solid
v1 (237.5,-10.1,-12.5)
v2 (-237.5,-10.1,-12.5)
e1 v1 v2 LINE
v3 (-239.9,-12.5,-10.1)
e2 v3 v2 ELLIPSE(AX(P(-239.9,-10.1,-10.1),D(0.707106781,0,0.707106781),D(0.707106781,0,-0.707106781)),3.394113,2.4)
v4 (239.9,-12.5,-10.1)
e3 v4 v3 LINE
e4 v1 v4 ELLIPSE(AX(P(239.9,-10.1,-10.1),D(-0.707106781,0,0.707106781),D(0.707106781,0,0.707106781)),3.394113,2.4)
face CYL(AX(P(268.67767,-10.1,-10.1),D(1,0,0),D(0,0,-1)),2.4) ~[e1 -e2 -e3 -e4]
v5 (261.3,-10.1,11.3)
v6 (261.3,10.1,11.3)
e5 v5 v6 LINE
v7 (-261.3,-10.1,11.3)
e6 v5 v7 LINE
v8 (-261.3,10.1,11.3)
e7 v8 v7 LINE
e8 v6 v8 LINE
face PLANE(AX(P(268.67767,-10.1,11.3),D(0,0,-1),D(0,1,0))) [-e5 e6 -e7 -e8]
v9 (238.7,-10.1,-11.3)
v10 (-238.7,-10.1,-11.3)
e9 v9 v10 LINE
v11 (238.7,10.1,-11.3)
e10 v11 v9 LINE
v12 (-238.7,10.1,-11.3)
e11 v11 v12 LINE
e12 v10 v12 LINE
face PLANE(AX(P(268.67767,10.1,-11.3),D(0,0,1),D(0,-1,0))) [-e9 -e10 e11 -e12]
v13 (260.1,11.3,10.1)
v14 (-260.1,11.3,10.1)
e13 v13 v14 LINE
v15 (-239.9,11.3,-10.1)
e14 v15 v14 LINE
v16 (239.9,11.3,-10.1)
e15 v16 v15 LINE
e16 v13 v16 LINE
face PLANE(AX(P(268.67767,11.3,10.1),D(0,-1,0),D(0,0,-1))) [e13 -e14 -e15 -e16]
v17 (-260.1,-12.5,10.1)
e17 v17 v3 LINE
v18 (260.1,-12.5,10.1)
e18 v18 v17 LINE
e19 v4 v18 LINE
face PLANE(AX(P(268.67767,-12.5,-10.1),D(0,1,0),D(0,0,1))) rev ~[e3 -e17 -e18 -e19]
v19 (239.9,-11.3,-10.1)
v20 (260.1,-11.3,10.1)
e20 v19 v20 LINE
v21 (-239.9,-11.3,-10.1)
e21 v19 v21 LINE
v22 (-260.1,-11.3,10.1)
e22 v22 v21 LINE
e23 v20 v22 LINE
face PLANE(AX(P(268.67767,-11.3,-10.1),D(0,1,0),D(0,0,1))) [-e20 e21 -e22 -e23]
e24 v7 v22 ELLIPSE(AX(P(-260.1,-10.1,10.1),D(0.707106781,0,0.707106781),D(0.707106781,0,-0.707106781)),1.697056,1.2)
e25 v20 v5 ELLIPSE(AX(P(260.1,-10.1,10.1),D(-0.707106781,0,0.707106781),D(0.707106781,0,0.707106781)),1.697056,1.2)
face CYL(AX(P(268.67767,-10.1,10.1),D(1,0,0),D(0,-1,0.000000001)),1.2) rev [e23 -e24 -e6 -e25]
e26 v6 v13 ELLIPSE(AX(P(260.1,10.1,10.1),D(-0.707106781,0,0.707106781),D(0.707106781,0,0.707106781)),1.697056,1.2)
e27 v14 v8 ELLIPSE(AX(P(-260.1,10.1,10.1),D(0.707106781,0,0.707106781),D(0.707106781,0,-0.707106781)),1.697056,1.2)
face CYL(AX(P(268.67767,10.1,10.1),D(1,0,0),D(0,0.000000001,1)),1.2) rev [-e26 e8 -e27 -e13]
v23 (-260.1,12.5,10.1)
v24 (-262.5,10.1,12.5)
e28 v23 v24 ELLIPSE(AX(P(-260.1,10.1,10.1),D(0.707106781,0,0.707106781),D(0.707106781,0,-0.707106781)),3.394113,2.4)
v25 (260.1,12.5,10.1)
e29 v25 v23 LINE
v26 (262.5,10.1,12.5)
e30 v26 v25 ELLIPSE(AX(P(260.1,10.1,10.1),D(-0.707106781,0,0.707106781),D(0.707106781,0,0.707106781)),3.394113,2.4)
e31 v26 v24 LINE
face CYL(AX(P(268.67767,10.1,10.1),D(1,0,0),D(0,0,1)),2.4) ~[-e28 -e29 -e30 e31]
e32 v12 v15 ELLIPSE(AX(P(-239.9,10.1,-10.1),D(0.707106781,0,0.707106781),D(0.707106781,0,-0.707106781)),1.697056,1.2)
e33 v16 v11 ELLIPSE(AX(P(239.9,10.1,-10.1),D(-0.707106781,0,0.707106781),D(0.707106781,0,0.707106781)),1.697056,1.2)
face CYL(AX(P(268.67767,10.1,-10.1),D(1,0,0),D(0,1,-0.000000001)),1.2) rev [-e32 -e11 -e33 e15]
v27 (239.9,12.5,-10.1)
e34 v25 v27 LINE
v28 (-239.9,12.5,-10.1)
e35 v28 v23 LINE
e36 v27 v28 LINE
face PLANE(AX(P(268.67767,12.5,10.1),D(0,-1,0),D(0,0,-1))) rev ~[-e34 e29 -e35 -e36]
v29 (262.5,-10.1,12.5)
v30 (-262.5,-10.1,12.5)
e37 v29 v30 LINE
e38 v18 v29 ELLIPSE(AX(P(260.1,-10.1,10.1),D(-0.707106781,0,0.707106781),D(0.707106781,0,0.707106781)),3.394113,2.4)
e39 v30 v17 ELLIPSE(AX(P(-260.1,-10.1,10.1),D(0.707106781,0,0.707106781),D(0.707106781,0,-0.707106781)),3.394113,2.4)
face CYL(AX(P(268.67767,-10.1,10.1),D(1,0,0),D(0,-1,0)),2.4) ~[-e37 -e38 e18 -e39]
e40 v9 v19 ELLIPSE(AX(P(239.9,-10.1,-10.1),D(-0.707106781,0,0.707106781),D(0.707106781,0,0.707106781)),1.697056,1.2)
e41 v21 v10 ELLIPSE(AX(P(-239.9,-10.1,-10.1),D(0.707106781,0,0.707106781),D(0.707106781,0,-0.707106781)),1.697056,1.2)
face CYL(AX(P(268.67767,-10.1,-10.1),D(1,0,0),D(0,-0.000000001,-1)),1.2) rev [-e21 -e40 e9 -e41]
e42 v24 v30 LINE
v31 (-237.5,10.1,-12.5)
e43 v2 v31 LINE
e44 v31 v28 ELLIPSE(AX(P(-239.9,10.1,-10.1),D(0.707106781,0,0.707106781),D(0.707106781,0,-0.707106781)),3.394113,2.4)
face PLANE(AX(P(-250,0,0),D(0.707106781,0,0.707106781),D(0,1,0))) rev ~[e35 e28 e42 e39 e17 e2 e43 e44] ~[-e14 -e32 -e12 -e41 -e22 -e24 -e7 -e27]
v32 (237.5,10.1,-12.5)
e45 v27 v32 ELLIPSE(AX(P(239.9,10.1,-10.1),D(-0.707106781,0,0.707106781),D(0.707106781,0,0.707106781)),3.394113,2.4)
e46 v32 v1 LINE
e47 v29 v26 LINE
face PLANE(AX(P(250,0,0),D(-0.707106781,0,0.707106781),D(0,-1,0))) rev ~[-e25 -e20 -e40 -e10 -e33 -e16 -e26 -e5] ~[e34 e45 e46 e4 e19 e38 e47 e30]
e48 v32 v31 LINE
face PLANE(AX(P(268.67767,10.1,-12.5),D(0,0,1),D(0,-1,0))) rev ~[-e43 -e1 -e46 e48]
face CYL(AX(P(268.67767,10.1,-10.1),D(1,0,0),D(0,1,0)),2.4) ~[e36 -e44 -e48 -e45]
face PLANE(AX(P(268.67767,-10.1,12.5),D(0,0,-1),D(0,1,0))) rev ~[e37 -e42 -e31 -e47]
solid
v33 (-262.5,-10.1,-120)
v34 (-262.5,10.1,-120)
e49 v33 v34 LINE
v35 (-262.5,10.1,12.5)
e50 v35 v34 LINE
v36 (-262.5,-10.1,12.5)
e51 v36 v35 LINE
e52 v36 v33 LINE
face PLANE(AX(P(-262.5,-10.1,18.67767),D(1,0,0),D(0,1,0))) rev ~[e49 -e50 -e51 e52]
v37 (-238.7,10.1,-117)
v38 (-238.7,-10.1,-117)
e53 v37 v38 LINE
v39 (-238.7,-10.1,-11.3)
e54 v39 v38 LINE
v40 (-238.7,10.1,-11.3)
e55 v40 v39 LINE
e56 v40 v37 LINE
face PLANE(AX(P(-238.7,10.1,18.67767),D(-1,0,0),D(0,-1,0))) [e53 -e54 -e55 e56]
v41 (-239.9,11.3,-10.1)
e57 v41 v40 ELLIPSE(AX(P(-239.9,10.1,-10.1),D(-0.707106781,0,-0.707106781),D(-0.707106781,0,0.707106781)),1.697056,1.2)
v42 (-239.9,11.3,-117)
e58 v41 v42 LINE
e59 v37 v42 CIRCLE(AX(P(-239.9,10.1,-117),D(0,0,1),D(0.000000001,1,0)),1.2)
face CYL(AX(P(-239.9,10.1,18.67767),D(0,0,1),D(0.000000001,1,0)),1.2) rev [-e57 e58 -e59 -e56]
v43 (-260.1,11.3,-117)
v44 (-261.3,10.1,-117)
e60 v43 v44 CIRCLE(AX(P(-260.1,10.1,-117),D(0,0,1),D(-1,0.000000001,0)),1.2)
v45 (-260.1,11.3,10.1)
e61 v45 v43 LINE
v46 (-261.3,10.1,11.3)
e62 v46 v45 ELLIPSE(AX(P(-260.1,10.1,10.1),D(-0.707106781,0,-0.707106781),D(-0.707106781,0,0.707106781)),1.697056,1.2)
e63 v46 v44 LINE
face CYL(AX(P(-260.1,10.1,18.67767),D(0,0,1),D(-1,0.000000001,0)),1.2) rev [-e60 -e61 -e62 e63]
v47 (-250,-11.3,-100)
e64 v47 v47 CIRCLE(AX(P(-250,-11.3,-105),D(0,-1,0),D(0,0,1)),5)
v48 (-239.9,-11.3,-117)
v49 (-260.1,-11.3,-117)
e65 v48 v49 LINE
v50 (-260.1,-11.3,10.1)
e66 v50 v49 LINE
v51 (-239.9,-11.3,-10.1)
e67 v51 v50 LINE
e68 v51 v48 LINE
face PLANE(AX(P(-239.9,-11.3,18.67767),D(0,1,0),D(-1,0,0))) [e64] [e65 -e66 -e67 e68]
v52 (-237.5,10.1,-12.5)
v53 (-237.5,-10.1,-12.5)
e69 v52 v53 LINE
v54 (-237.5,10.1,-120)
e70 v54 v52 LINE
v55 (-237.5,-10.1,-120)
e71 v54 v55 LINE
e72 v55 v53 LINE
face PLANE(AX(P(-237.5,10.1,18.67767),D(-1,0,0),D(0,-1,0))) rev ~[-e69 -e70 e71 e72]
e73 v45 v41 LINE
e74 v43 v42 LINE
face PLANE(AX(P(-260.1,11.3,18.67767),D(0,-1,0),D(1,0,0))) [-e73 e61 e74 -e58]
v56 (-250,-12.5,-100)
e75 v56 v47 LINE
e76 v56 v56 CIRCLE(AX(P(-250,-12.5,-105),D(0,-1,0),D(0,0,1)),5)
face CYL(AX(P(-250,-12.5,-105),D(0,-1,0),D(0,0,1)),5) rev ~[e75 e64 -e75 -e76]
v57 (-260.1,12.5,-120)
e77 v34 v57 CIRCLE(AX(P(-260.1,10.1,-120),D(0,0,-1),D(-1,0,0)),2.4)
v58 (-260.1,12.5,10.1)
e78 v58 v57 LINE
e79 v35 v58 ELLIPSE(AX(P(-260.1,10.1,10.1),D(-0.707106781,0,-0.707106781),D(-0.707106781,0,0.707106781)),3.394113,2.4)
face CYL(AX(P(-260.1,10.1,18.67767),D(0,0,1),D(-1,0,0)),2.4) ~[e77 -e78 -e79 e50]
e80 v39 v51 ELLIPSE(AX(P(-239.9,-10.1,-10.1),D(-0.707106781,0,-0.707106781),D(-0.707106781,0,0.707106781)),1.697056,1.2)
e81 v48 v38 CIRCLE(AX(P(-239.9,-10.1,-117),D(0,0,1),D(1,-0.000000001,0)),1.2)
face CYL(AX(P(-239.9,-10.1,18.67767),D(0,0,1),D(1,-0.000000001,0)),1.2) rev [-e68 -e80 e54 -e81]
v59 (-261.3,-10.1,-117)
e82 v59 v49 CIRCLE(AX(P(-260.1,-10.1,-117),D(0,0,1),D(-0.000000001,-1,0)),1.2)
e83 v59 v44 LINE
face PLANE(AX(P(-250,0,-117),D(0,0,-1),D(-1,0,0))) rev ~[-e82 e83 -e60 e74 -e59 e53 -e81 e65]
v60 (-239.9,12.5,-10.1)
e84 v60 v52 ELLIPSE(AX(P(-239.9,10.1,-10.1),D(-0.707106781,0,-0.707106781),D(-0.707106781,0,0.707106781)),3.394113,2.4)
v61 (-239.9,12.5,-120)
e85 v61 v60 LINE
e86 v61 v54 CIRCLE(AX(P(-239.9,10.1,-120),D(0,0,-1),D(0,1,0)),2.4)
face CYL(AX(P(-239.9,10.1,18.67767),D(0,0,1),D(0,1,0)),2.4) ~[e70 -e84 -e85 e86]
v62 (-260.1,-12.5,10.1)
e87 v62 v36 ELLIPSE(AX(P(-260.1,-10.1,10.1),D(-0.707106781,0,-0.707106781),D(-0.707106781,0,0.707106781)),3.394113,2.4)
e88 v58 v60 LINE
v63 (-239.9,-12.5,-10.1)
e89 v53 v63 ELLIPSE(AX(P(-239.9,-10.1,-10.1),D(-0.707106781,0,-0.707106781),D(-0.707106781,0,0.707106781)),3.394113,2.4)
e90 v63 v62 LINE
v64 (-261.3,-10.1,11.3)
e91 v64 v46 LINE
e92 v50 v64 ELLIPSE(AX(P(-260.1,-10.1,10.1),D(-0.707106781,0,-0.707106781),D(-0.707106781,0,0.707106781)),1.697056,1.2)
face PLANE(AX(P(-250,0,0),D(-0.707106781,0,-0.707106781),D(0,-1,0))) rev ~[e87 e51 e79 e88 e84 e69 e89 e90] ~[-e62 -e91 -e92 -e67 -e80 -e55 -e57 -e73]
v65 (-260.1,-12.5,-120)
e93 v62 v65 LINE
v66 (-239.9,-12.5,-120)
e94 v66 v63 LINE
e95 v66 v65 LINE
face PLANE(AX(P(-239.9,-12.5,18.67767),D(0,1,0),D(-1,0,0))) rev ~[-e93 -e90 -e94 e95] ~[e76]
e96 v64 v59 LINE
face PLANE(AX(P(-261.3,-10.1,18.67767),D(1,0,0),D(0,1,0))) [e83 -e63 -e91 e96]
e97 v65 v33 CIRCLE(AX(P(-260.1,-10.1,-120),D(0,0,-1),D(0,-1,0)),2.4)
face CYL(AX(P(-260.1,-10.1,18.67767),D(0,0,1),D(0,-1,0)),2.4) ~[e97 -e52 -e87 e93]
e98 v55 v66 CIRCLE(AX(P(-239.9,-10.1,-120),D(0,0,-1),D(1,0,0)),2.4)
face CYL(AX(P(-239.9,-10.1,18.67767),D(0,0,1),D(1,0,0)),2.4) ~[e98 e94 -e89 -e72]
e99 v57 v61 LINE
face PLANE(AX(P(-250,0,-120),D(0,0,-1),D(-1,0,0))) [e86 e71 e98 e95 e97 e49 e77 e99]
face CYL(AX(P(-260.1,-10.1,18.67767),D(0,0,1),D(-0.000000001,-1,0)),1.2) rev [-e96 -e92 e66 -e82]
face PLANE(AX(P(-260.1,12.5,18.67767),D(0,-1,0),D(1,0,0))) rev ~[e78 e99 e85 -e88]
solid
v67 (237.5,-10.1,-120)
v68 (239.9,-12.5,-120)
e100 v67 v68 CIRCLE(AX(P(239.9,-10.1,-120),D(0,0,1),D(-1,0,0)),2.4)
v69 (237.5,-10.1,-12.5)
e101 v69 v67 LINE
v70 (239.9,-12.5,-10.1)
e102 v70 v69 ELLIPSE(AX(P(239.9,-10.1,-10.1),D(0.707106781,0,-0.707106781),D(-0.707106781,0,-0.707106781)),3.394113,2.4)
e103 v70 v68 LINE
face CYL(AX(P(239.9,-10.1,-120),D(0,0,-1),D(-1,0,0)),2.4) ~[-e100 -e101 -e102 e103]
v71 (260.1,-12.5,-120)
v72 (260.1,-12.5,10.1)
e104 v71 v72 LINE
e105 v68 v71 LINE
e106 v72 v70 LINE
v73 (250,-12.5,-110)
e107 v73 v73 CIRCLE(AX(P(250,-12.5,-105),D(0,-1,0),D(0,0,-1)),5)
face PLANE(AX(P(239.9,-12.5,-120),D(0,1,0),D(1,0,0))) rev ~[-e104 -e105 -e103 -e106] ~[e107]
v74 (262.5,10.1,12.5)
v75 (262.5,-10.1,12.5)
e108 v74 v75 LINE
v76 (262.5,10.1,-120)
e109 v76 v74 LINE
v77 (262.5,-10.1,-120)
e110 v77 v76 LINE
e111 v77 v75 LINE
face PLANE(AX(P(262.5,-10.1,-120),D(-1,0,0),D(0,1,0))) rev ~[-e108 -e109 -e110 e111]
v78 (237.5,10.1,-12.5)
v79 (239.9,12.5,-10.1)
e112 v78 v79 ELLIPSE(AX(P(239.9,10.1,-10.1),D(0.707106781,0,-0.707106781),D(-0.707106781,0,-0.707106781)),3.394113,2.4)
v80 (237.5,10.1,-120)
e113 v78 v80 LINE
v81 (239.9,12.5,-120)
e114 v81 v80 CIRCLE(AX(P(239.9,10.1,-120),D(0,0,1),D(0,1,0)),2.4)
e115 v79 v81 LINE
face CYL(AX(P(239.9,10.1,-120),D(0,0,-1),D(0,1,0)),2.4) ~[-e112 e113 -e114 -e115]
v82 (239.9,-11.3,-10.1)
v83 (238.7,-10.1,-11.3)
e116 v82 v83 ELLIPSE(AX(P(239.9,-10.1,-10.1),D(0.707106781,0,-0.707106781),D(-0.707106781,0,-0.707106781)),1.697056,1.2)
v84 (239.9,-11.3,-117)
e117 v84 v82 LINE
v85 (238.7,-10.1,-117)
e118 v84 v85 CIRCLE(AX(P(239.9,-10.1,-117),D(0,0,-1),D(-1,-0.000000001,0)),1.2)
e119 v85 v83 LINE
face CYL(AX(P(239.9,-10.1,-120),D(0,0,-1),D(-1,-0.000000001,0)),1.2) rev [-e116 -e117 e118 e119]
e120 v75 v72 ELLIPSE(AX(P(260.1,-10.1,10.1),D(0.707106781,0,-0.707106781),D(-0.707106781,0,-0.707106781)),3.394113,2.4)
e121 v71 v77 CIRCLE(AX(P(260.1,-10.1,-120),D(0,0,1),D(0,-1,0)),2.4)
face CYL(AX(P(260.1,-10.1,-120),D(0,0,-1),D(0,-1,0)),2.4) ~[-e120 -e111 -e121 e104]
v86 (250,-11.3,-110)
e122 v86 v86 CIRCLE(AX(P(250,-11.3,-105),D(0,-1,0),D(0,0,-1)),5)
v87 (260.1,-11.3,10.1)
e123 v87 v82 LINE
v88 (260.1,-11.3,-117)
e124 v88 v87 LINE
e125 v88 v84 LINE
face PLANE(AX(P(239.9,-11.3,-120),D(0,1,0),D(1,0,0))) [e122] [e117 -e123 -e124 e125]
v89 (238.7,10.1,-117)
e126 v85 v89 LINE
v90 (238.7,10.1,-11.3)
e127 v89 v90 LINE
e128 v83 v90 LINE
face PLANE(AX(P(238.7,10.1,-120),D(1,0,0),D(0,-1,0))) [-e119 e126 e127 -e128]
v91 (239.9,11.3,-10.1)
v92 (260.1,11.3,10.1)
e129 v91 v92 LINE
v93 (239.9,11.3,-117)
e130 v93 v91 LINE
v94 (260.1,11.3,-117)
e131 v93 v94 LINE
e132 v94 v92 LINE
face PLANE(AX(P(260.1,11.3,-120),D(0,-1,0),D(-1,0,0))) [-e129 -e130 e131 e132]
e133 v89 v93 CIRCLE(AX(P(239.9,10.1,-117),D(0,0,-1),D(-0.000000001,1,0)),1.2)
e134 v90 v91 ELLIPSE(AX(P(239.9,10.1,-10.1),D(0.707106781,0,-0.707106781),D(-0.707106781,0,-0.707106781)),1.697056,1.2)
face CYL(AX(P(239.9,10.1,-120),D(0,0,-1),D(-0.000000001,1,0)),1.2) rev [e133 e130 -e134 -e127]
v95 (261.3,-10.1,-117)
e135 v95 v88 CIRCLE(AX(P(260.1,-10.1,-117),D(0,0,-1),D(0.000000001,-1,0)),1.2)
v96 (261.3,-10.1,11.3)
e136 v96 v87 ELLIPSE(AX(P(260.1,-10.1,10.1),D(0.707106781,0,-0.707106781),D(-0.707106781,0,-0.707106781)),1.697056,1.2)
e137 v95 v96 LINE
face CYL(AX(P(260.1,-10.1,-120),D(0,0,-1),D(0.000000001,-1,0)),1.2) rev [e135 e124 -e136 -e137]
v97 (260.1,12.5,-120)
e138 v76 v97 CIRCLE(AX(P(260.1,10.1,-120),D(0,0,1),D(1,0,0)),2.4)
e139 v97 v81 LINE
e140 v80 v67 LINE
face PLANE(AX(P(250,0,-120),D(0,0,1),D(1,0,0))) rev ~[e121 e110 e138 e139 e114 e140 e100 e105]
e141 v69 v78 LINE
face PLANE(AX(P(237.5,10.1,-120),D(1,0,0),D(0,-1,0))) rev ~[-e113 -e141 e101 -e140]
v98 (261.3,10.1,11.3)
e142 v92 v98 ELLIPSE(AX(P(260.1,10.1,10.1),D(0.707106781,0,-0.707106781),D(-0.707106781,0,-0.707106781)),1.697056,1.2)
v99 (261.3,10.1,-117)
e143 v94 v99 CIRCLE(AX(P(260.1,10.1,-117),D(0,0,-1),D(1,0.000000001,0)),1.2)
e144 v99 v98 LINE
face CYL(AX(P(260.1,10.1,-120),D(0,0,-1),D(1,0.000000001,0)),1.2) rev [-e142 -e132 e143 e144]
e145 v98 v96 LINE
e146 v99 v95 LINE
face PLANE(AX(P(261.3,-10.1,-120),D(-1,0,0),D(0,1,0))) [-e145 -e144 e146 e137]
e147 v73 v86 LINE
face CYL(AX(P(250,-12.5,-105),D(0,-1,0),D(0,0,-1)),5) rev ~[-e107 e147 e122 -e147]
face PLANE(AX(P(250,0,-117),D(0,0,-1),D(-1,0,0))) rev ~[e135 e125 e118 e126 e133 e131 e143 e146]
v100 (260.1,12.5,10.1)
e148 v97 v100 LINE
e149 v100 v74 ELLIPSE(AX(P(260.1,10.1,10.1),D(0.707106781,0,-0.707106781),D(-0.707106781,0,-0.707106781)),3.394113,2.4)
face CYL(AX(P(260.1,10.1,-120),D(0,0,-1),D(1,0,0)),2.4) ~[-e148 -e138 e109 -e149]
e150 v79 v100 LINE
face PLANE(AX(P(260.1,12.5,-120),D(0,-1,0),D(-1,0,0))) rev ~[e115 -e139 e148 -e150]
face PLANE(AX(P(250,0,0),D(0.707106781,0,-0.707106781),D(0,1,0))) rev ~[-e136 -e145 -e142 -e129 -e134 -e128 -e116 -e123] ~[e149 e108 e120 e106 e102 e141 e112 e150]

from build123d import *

# Parameters (mm, degrees)
GB_6728_1986_SQUARE_HOLLOW_SECTION_025_X_DEPTH    = 138.67766953
GB_6728_1986_SQUARE_HOLLOW_SECTION_0_3_DEPTH      = 537.355339059
GB_6728_1986_SQUARE_HOLLOW_SECTION_0_5_DEPTH      = 120
GB_6728_1986_SQUARE_HOLLOW_SECTION_0_5_DEPTH_BACK = 18.67766953
BOSS_EXTRUDE1_DEPTH                               = 3
SKETCH3_R                                         = 5
CUT_EXTRUDE1_DEPTH                                = 2


with BuildPart() as part:
    # Sketch11 on segment 1 (carried to segment 1) → Gb／6728-1986 square hollow section 025 X 25 X 1.2(1) (new body)
    with BuildSketch(Plane(origin=(250, 0, -120), x_dir=(1, 0, 0), z_dir=(0, 0, 1))):
        with BuildLine():
            Line((-10.1, -12.5), (10.1, -12.5))
            ThreePointArc((10.1, -12.5), (11.797056275, -11.797056275), (12.5, -10.1))
            Line((12.5, -10.1), (12.5, 10.1))
            ThreePointArc((12.5, 10.1), (11.797056275, 11.797056275), (10.1, 12.5))
            Line((10.1, 12.5), (-10.1, 12.5))
            ThreePointArc((-10.1, 12.5), (-11.797056275, 11.797056275), (-12.5, 10.1))
            Line((-12.5, 10.1), (-12.5, -10.1))
            ThreePointArc((-12.5, -10.1), (-11.797056275, -11.797056275), (-10.1, -12.5))
        make_face()
        with BuildLine():
            Line((-10.1, -11.3), (10.1, -11.3))
            ThreePointArc((10.1, -11.3), (10.948528137, -10.948528137), (11.3, -10.1))
            Line((11.3, -10.1), (11.3, 10.1))
            ThreePointArc((11.3, 10.1), (10.948528137, 10.948528137), (10.1, 11.3))
            Line((10.1, 11.3), (-10.1, 11.3))
            ThreePointArc((-10.1, 11.3), (-10.948528137, 10.948528137), (-11.3, 10.1))
            Line((-11.3, 10.1), (-11.3, -10.1))
            ThreePointArc((-11.3, -10.1), (-10.948528137, -10.948528137), (-10.1, -11.3))
        make_face(mode=Mode.SUBTRACT)
    extrude(amount=GB_6728_1986_SQUARE_HOLLOW_SECTION_025_X_DEPTH)

    # Gb_6728-1986 square hollow section 0 2
    split(bisect_by=Plane(origin=(250, 0, 0), x_dir=(0, 1, 0), z_dir=(0.707106781, 0, -0.707106781)), keep=Keep.TOP)



with BuildPart() as body_2:
    # Sketch11 on segment 2 (carried to segment 2) → Gb_6728-1986 square hollow section 0 3 (new body)
    with BuildSketch(Plane.ZY.offset(-268.67766953)):
        with BuildLine():
            Line((-10.1, -12.5), (10.1, -12.5))
            ThreePointArc((10.1, -12.5), (11.797056275, -11.797056275), (12.5, -10.1))
            Line((12.5, -10.1), (12.5, 10.1))
            ThreePointArc((12.5, 10.1), (11.797056275, 11.797056275), (10.1, 12.5))
            Line((10.1, 12.5), (-10.1, 12.5))
            ThreePointArc((-10.1, 12.5), (-11.797056275, 11.797056275), (-12.5, 10.1))
            Line((-12.5, 10.1), (-12.5, -10.1))
            ThreePointArc((-12.5, -10.1), (-11.797056275, -11.797056275), (-10.1, -12.5))
        make_face()
        with BuildLine():
            Line((-10.1, -11.3), (10.1, -11.3))
            ThreePointArc((10.1, -11.3), (10.948528137, -10.948528137), (11.3, -10.1))
            Line((11.3, -10.1), (11.3, 10.1))
            ThreePointArc((11.3, 10.1), (10.948528137, 10.948528137), (10.1, 11.3))
            Line((10.1, 11.3), (-10.1, 11.3))
            ThreePointArc((-10.1, 11.3), (-10.948528137, 10.948528137), (-11.3, 10.1))
            Line((-11.3, 10.1), (-11.3, -10.1))
            ThreePointArc((-11.3, -10.1), (-10.948528137, -10.948528137), (-10.1, -11.3))
        make_face(mode=Mode.SUBTRACT)
    extrude(amount=GB_6728_1986_SQUARE_HOLLOW_SECTION_0_3_DEPTH)

    # Gb_6728-1986 square hollow section 0 3 m
    split(bisect_by=Plane(origin=(-250, 0, 0), x_dir=(0, 1, 0), z_dir=(0.707106781, 0, 0.707106781)), keep=Keep.TOP)

    # Gb_6728-1986 square hollow section 0 4
    split(bisect_by=Plane(origin=(250, 0, 0), x_dir=(0, -1, 0), z_dir=(-0.707106781, 0, 0.707106781)), keep=Keep.TOP)


with BuildPart() as body_3:
    # Sketch11 → Gb_6728-1986 square hollow section 0 5 (new, two sides: drawn at the far end of the back side and taken through both)
    with BuildSketch(Plane(origin=(-250, 0, 0), x_dir=(-1, 0, 0), z_dir=(0, 0, -1)).offset(-GB_6728_1986_SQUARE_HOLLOW_SECTION_0_5_DEPTH_BACK)):
        with BuildLine():
            Line((-10.1, -12.5), (10.1, -12.5))
            ThreePointArc((10.1, -12.5), (11.797056275, -11.797056275), (12.5, -10.1))
            Line((12.5, -10.1), (12.5, 10.1))
            ThreePointArc((12.5, 10.1), (11.797056275, 11.797056275), (10.1, 12.5))
            Line((10.1, 12.5), (-10.1, 12.5))
            ThreePointArc((-10.1, 12.5), (-11.797056275, 11.797056275), (-12.5, 10.1))
            Line((-12.5, 10.1), (-12.5, -10.1))
            ThreePointArc((-12.5, -10.1), (-11.797056275, -11.797056275), (-10.1, -12.5))
        make_face()
        with BuildLine():
            Line((-10.1, -11.3), (10.1, -11.3))
            ThreePointArc((10.1, -11.3), (10.948528137, -10.948528137), (11.3, -10.1))
            Line((11.3, -10.1), (11.3, 10.1))
            ThreePointArc((11.3, 10.1), (10.948528137, 10.948528137), (10.1, 11.3))
            Line((10.1, 11.3), (-10.1, 11.3))
            ThreePointArc((-10.1, 11.3), (-10.948528137, 10.948528137), (-11.3, 10.1))
            Line((-11.3, 10.1), (-11.3, -10.1))
            ThreePointArc((-11.3, -10.1), (-10.948528137, -10.948528137), (-10.1, -11.3))
        make_face(mode=Mode.SUBTRACT)
    extrude(amount=GB_6728_1986_SQUARE_HOLLOW_SECTION_0_5_DEPTH + GB_6728_1986_SQUARE_HOLLOW_SECTION_0_5_DEPTH_BACK)

    # Gb_6728-1986 square hollow section 0 5 m
    split(bisect_by=Plane(origin=(-250, 0, 0), x_dir=(0, -1, 0), z_dir=(-0.707106781, 0, -0.707106781)), keep=Keep.TOP)


with BuildPart() as part_1:
    add(part.part)

    add(body_3.part)  # Boss-Extrude1 merges body 3
    # Sketch2 → Boss-Extrude1 (add)
    with BuildSketch(Plane(origin=(0, 0, -120), x_dir=(-1, 0, 0), z_dir=(0, 0, -1))):
        with BuildLine():
            Line((-262.5, 10.1), (-262.5, -10.1))
            ThreePointArc((-262.5, -10.1), (-261.797056275, -11.797056275), (-260.1, -12.5))
            Line((-260.1, -12.5), (-239.9, -12.5))
            ThreePointArc((-239.9, -12.5), (-238.202943725, -11.797056275), (-237.5, -10.1))
            Line((-237.5, -10.1), (-237.5, 10.1))
            ThreePointArc((-237.5, 10.1), (-238.202943725, 11.797056275), (-239.9, 12.5))
            Line((-239.9, 12.5), (-260.1, 12.5))
            ThreePointArc((-260.1, 12.5), (-261.797056275, 11.797056275), (-262.5, 10.1))
        make_face()
        with BuildLine():
            Line((260.1, 12.5), (239.9, 12.5))
            ThreePointArc((239.9, 12.5), (238.202943725, 11.797056275), (237.5, 10.1))
            Line((237.5, 10.1), (237.5, -10.1))
            ThreePointArc((237.5, -10.1), (238.202943725, -11.797056275), (239.9, -12.5))
            Line((239.9, -12.5), (260.1, -12.5))
            ThreePointArc((260.1, -12.5), (261.797056275, -11.797056275), (262.5, -10.1))
            Line((262.5, -10.1), (262.5, 10.1))
            ThreePointArc((262.5, 10.1), (261.797056275, 11.797056275), (260.1, 12.5))
        make_face()
    extrude(amount=-BOSS_EXTRUDE1_DEPTH)

    # Sketch3 → Cut-Extrude1 (cut)
    with BuildSketch(Plane.XZ.offset(12.5)):
        with Locations(Location((250, -105, 0), (0, 0, 270))):
            Circle(SKETCH3_R)
        with Locations(Location((-250, -105, 0), (0, 0, 90))):
            Circle(SKETCH3_R)
    extrude(amount=-CUT_EXTRUDE1_DEPTH, mode=Mode.SUBTRACT)


solid = Compound([body_2.part, part_1.part])
